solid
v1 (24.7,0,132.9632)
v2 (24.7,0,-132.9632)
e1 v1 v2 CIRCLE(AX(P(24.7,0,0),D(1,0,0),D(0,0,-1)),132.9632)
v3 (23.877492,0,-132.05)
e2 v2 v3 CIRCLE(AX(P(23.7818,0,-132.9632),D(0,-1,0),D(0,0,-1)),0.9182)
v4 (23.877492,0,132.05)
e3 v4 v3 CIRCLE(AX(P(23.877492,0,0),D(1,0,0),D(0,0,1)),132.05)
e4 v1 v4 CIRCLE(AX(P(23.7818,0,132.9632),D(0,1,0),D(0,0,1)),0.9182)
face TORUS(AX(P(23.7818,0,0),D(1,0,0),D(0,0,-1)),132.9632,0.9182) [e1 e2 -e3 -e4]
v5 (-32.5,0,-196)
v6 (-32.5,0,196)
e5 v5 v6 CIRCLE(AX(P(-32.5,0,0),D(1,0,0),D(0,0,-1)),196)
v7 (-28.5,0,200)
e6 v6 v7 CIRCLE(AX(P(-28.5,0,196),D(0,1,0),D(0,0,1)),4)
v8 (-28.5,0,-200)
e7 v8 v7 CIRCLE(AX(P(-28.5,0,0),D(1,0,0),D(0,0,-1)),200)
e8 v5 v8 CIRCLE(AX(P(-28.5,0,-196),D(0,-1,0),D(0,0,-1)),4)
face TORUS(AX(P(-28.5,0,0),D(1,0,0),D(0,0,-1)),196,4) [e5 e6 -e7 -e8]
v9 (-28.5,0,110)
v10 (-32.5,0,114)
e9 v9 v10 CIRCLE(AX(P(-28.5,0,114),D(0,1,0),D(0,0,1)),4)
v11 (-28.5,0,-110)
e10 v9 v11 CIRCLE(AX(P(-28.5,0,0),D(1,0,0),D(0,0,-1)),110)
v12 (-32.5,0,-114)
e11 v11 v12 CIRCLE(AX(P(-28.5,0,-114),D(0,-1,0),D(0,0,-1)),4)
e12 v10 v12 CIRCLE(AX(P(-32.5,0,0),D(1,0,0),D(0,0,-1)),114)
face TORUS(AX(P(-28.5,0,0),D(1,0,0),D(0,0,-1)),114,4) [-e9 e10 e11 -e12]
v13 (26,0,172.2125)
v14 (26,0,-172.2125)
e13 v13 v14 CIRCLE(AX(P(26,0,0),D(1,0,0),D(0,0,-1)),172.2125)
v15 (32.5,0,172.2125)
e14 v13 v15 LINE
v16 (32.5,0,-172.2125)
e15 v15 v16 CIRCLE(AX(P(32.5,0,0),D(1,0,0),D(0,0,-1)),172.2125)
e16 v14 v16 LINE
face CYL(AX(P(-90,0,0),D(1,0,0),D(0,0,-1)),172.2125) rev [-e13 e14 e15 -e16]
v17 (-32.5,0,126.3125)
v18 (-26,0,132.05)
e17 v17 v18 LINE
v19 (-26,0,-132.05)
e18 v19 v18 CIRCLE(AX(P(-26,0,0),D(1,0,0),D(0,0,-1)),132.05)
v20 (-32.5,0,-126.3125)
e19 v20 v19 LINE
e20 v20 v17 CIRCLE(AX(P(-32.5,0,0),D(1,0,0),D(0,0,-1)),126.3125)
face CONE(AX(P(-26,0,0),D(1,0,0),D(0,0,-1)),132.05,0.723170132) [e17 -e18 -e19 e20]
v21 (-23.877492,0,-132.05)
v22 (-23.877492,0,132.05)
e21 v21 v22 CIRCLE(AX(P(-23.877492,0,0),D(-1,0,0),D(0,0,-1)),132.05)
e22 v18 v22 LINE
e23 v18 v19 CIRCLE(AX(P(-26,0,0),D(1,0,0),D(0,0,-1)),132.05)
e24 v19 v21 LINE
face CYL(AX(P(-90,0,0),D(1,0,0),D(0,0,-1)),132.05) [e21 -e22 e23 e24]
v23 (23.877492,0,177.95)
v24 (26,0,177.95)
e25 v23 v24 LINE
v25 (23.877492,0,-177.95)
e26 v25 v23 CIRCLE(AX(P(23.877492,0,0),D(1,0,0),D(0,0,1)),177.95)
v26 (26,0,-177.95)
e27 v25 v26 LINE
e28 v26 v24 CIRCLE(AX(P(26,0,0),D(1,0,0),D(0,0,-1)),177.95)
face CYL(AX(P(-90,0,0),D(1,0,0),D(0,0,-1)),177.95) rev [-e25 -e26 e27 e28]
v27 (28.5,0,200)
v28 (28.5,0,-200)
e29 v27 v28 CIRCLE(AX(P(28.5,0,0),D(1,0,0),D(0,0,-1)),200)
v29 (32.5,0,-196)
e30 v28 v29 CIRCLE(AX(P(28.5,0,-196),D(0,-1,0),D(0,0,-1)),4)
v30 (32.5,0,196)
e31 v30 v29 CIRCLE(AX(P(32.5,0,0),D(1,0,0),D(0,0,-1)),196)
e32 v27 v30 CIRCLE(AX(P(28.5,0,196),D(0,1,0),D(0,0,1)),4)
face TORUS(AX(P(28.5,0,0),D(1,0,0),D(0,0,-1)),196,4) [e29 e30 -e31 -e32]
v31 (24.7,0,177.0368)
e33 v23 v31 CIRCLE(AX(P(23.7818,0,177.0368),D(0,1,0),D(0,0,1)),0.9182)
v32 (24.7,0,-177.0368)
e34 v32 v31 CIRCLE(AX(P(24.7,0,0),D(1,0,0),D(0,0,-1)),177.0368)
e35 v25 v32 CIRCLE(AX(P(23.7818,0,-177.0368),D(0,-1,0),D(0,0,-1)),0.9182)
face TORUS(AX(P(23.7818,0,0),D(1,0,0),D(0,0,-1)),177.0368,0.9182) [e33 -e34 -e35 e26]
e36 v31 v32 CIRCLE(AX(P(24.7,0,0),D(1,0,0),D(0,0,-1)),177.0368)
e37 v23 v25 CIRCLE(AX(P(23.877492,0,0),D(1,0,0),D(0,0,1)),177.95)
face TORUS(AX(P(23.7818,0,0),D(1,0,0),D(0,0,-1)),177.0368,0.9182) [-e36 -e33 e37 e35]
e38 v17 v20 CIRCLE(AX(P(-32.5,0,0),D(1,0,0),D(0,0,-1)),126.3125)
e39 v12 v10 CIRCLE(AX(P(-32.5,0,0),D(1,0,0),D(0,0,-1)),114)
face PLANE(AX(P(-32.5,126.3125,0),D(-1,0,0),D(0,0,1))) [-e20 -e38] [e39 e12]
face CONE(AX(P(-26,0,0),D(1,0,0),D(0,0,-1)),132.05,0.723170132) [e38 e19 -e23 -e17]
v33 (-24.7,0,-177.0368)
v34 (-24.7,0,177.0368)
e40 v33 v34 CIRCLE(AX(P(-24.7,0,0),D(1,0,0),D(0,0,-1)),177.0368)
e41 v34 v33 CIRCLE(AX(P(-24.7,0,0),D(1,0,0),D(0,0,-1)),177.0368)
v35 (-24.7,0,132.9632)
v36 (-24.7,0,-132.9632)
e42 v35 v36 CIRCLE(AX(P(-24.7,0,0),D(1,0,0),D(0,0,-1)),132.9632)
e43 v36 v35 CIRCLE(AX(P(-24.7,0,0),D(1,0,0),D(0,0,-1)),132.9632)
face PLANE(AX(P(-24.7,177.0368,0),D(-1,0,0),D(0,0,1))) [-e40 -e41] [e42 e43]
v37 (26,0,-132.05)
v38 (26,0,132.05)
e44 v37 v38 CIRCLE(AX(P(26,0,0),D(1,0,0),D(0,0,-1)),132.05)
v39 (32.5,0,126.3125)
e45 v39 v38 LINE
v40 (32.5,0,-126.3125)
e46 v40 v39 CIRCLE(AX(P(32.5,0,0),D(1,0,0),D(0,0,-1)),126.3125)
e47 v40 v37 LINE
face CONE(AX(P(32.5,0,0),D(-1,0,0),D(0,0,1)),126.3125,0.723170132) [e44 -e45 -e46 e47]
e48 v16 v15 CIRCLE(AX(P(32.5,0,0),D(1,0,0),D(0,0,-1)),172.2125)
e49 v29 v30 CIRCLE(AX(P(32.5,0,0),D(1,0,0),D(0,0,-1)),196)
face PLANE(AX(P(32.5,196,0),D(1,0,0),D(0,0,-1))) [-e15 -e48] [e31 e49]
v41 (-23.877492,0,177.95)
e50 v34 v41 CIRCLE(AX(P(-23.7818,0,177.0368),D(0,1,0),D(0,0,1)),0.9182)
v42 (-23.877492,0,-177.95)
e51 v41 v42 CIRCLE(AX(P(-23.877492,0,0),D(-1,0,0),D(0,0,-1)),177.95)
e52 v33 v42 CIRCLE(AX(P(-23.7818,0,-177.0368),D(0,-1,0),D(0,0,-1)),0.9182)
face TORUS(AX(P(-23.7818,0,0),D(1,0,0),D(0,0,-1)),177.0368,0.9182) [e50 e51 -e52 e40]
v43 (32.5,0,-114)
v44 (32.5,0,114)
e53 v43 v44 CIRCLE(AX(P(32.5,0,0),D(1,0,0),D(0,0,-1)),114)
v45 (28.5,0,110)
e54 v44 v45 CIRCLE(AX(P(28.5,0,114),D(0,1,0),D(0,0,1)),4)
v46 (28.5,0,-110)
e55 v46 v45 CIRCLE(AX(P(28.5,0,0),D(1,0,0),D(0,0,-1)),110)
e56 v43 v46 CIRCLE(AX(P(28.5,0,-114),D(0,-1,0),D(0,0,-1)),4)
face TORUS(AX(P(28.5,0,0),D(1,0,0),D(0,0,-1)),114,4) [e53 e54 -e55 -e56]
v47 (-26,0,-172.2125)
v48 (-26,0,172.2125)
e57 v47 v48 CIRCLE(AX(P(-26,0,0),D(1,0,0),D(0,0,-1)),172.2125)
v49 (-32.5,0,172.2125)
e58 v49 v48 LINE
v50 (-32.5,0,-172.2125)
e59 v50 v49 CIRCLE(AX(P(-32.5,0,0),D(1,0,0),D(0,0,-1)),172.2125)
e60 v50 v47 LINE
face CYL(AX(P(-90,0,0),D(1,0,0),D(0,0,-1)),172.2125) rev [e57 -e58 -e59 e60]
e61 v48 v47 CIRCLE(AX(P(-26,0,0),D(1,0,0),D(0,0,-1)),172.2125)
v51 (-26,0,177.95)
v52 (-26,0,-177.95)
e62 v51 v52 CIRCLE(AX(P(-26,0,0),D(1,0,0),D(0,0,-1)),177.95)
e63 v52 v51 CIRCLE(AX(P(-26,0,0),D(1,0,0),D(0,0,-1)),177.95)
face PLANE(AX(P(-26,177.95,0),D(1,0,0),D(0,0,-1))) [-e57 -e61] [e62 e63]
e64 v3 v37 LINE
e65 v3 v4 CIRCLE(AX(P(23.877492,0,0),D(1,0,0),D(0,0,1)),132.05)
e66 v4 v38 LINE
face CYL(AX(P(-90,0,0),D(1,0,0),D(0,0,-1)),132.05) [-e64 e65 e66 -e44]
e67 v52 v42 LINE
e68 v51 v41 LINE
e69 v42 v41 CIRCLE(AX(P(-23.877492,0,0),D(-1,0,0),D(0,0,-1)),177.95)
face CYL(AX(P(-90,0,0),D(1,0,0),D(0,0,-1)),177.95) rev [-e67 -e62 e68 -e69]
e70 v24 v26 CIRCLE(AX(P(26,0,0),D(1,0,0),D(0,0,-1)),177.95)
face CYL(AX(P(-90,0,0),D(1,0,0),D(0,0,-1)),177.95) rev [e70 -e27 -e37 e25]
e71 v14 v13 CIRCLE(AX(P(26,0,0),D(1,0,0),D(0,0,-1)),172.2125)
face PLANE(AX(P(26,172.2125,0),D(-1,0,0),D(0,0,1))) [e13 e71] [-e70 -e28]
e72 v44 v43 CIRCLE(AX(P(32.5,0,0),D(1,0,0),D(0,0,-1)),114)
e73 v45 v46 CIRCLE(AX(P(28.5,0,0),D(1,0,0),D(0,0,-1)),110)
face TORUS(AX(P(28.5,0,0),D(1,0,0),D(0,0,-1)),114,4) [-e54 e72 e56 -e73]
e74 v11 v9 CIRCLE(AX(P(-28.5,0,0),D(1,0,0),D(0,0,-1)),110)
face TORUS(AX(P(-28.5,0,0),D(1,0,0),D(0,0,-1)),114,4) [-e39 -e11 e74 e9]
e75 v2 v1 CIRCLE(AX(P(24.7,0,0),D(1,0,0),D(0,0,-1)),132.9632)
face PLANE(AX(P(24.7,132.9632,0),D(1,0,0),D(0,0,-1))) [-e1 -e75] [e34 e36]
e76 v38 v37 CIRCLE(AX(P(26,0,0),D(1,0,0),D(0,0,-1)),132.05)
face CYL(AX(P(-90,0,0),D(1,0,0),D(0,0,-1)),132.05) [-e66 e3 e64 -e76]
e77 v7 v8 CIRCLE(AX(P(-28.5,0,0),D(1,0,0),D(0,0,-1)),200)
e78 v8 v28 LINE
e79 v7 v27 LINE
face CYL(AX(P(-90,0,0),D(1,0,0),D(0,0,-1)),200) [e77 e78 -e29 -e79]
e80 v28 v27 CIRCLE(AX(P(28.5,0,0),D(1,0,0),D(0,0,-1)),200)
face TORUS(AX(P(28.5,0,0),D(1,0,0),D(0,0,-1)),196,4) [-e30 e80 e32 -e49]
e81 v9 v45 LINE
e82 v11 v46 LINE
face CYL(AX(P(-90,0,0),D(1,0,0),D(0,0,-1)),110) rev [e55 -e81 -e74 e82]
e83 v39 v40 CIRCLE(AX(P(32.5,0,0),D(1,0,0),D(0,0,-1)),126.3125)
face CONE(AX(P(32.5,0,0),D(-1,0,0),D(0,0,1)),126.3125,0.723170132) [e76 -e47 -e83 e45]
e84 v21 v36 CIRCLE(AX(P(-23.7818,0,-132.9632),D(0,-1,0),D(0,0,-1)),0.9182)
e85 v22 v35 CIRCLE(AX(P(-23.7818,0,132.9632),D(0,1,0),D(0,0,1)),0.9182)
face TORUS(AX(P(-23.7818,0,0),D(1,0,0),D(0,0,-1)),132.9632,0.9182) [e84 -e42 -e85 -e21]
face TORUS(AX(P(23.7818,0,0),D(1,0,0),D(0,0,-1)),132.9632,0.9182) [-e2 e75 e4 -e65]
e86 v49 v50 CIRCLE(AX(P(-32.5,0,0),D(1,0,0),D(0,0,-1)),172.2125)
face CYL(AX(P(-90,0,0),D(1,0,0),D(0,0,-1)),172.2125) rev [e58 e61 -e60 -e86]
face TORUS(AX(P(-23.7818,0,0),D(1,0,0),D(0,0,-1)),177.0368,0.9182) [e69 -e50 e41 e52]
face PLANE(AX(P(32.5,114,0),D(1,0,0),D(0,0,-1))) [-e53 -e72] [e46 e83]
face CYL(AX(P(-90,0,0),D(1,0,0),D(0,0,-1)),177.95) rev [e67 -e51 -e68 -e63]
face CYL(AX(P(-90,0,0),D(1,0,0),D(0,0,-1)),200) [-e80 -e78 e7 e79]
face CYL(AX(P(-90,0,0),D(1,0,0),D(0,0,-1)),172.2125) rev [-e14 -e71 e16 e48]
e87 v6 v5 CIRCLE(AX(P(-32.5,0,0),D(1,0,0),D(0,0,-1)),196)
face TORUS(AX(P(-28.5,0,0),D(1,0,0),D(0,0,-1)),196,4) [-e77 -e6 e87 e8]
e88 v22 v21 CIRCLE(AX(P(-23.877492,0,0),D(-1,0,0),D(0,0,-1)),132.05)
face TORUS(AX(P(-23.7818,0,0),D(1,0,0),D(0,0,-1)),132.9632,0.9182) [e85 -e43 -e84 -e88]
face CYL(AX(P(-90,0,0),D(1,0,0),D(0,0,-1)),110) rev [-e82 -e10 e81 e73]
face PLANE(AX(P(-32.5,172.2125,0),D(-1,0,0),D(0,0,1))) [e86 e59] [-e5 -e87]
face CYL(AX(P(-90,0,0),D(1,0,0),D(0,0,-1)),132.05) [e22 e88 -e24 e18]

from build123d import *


with BuildPart() as part:
    # OutRacSke → OuterRace (revolve)
    with BuildSketch(Plane.XY, mode=Mode.PRIVATE) as outerrace_sk:
        with BuildLine():
            Line((-26, 172.2125), (-32.5, 172.2125))
            Line((-32.5, 172.2125), (-32.5, 196))
            ThreePointArc((-32.5, 196), (-31.328427125, 198.828427125), (-28.5, 200))
            Line((-28.5, 200), (28.5, 200))
            ThreePointArc((28.5, 200), (31.328427125, 198.828427125), (32.5, 196))
            Line((32.5, 196), (32.5, 172.2125))
            Line((32.5, 172.2125), (26, 172.2125))
            Line((26, 172.2125), (26, 177.95))
            Line((26, 177.95), (-26, 177.95))
            Line((-26, 177.95), (-26, 172.2125))
        make_face()
    revolve(outerrace_sk.sketch.rotate(Axis((-90, 0, 0), (1, 0, 0)), 270), axis=Axis((-90, 0, 0), (1, 0, 0)))

    # RolSimSke → RollersSimplified (revolve)
    with BuildSketch(Plane(origin=(0, 101.6, 0), x_dir=(1, 0, 0), z_dir=(0, 0, 1)), mode=Mode.PRIVATE) as rollerssimplified_sk:
        with BuildLine():
            Line((-24.7, 75.4368), (-24.7, 31.3632))
            ThreePointArc((-24.7, 31.3632), (-24.431065446, 30.713934554), (-23.7818, 30.445))
            Line((-23.7818, 30.445), (23.7818, 30.445))
            ThreePointArc((23.7818, 30.445), (24.431065446, 30.713934554), (24.7, 31.3632))
            Line((24.7, 31.3632), (24.7, 75.4368))
            ThreePointArc((24.7, 75.4368), (24.431065446, 76.086065446), (23.7818, 76.355))
            Line((23.7818, 76.355), (-23.7818, 76.355))
            ThreePointArc((-23.7818, 76.355), (-24.431065446, 76.086065446), (-24.7, 75.4368))
        make_face()
    revolve(rollerssimplified_sk.sketch.rotate(Axis((25.4, 0, 0), (-1, 0, 0)), 90), axis=Axis((25.4, 0, 0), (-1, 0, 0)))

    # InsRacSke → InnerRace (revolve)
    with BuildSketch(Plane.XY, mode=Mode.PRIVATE) as innerrace_sk:
        with BuildLine():
            Line((-26, 132.05), (-32.5, 126.3125))
            Line((-32.5, 126.3125), (-32.5, 114))
            ThreePointArc((-32.5, 114), (-31.328427125, 111.171572875), (-28.5, 110))
            Line((-28.5, 110), (28.5, 110))
            ThreePointArc((28.5, 110), (31.328427125, 111.171572875), (32.5, 114))
            Line((32.5, 114), (32.5, 126.3125))
            Line((32.5, 126.3125), (26, 132.05))
            Line((26, 132.05), (-26, 132.05))
        make_face()
    revolve(innerrace_sk.sketch.rotate(Axis((-90, 0, 0), (1, 0, 0)), 270), axis=Axis((-90, 0, 0), (1, 0, 0)))


solid = part.part
